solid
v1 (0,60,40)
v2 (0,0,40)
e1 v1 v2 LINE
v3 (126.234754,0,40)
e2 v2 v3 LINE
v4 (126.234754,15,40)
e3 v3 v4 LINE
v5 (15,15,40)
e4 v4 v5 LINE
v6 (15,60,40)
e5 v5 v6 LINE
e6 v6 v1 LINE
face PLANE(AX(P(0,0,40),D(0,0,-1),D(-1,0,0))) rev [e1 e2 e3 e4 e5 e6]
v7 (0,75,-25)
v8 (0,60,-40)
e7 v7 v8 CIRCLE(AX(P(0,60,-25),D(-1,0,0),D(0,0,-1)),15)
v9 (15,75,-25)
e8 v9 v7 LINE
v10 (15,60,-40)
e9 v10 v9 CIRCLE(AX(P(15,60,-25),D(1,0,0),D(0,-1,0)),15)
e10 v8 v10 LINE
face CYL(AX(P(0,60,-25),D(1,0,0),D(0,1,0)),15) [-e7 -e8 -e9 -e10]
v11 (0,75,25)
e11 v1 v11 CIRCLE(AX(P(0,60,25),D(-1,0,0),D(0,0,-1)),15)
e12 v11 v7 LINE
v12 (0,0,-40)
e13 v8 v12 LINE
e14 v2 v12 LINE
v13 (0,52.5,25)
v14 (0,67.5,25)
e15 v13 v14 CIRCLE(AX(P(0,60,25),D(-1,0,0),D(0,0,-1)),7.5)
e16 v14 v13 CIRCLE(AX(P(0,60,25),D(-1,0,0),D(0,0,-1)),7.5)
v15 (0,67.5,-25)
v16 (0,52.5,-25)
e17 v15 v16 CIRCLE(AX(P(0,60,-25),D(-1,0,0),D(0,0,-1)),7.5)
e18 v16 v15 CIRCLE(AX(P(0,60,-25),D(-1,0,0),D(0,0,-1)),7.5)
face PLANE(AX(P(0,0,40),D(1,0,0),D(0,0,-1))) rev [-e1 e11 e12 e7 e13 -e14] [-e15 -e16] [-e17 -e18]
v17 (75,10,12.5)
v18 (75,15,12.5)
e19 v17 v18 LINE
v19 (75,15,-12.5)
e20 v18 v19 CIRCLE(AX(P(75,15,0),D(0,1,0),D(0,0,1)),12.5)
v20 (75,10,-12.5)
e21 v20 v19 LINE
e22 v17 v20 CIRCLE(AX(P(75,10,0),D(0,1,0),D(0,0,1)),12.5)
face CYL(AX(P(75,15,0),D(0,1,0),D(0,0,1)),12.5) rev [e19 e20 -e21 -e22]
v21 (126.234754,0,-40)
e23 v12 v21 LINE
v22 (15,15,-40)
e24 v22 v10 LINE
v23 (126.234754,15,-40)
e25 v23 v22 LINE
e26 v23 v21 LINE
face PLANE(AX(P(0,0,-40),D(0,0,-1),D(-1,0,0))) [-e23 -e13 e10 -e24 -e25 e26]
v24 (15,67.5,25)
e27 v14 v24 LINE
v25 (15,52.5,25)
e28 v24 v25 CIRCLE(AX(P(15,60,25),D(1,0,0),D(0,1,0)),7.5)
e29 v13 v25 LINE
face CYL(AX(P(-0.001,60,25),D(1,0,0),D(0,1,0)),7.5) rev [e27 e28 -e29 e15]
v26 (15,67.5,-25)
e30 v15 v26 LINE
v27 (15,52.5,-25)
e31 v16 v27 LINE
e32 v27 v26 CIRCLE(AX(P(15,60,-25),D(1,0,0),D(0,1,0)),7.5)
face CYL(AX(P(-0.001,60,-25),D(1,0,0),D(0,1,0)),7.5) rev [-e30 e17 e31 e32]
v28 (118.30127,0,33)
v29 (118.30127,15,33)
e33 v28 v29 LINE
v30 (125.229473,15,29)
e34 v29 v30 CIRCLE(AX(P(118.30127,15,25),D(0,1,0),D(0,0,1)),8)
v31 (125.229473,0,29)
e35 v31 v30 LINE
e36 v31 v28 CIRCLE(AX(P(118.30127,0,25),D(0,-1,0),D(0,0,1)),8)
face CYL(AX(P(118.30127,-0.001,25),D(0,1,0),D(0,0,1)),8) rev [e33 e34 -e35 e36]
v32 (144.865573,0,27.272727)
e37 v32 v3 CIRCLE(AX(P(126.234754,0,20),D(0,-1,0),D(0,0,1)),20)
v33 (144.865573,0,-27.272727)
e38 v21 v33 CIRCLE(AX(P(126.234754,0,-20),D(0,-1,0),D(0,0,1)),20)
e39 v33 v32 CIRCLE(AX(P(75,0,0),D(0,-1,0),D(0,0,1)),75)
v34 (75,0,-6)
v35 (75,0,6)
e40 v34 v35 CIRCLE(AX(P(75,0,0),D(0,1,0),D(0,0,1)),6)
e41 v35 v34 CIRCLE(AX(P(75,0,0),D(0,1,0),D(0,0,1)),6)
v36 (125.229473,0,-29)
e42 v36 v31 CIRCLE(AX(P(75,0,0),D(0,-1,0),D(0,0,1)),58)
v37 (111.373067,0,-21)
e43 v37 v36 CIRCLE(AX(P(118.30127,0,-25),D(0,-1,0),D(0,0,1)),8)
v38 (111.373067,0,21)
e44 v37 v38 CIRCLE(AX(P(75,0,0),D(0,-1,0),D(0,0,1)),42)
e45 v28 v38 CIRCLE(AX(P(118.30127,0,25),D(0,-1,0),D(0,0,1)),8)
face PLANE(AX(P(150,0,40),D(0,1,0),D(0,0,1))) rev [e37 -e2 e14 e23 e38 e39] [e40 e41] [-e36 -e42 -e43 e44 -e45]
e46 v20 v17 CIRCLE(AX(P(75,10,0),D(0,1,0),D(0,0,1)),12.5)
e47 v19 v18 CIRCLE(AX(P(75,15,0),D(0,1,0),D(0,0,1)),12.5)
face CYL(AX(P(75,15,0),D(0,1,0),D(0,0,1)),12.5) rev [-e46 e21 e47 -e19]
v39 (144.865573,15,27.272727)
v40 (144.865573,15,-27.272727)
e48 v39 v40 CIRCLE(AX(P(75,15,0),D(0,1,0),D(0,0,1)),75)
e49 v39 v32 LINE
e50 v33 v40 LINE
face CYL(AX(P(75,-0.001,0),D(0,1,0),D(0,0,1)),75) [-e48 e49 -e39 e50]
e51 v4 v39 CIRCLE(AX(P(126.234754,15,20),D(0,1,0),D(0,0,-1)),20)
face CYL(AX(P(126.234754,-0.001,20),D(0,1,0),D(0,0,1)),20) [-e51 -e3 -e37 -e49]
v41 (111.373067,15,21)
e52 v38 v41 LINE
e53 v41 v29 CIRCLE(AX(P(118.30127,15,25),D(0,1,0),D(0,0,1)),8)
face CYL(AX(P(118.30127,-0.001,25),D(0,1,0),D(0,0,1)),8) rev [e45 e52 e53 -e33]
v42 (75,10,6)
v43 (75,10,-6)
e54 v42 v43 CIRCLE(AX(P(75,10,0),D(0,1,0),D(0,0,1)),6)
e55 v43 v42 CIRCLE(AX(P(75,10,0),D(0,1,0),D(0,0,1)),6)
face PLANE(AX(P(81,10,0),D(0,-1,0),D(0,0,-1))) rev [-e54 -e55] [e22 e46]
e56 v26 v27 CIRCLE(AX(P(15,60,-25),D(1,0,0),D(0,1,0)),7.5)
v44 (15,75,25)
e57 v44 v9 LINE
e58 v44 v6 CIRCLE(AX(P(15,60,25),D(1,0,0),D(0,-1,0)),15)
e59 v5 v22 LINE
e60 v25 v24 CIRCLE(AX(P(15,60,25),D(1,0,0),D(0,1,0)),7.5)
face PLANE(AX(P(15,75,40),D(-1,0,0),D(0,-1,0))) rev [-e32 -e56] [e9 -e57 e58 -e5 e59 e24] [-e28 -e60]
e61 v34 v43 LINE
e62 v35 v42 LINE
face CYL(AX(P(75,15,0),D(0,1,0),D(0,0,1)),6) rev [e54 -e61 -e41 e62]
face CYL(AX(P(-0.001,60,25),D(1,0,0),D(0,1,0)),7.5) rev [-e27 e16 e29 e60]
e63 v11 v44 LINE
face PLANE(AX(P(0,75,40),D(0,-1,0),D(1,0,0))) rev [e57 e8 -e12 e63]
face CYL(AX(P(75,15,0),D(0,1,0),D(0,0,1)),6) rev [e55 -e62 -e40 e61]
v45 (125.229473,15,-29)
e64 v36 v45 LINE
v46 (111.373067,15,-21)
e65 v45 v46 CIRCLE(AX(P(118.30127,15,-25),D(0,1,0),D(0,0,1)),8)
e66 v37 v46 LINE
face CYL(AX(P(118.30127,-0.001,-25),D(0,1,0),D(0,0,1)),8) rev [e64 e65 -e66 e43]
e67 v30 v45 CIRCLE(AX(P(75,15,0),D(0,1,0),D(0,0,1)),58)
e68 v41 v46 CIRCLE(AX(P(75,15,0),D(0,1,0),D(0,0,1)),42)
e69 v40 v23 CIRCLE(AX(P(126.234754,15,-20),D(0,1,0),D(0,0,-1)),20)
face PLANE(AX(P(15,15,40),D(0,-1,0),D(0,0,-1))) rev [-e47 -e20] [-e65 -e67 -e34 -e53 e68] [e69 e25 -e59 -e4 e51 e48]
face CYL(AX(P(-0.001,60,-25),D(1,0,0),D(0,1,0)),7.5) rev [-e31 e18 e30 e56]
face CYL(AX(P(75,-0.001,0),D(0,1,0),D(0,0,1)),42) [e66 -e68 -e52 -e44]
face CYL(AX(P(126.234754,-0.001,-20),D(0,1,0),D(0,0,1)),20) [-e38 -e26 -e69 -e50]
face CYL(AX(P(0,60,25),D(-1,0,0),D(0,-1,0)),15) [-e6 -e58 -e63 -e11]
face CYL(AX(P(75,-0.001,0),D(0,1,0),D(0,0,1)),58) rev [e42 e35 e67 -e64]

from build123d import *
from OCP.BRepFilletAPI import BRepFilletAPI_MakeFillet

# Parameters (mm, degrees)
L_BRACKET_BODY_DEPTH             = 40
ARC_SLOT_R50_30DEG_REACH         = 168.433
CORNER_ROUNDS_R1                 = 20
CORNER_ROUNDS_R2                 = 15
COUNTERBORED_HOLE_12_D           = 12
COUNTERBORED_HOLE_12_DEPTH       = 100
COUNTERBORED_HOLE_12_CBORE_D     = 25
COUNTERBORED_HOLE_12_CBORE_DEPTH = 5
UPRIGHT_HOLES_2X_REACH           = 161.531
UPRIGHT_HOLES_SKETCH_R           = 7.5


with BuildPart() as part:
    # L Profile Sketch → L Bracket Body (new, symmetric)
    with BuildSketch(Plane.XY):
        Polygon((0, 0), (0, 75), (15, 75), (15, 15), (150, 15), (150, 0), align=None)
    extrude(amount=L_BRACKET_BODY_DEPTH, both=True)

    # Arc Slot Sketch → Arc Slot R50 30deg (cut, up to next)
    with BuildSketch(Plane(origin=(0, 15, 0), x_dir=(1, 0, 0), z_dir=(0, 1, 0)), mode=Mode.PRIVATE) as arc_slot_r50_30deg_sk1:
        with BuildLine():
            Line((138.442887702, -40), (150, -40))
            Line((150, -40), (150, 0))
            ThreePointArc((150, 0), (147.052815967, -20.818062138), (138.442887702, -40))
        make_face()
    arc_slot_r50_30deg_tool1 = extrude(arc_slot_r50_30deg_sk1.sketch, amount=-ARC_SLOT_R50_30DEG_REACH, mode=Mode.PRIVATE) & part.part
    # Arc Slot Sketch → Arc Slot R50 30deg (cut, up to next)
    with BuildSketch(Plane(origin=(0, 15, 0), x_dir=(1, 0, 0), z_dir=(0, 1, 0)), mode=Mode.PRIVATE) as arc_slot_r50_30deg_sk2:
        with BuildLine():
            ThreePointArc((138.442887702, 40), (147.052815967, 20.818062138), (150, 0))
            Line((150, 0), (150, 40))
            Line((150, 40), (138.442887702, 40))
        make_face()
    arc_slot_r50_30deg_tool2 = extrude(arc_slot_r50_30deg_sk2.sketch, amount=-ARC_SLOT_R50_30DEG_REACH, mode=Mode.PRIVATE) & part.part
    # Arc Slot Sketch → Arc Slot R50 30deg (cut, up to next)
    with BuildSketch(Plane(origin=(0, 15, 0), x_dir=(1, 0, 0), z_dir=(0, 1, 0)), mode=Mode.PRIVATE) as arc_slot_r50_30deg_sk3:
        with BuildLine():
            ThreePointArc((125.229473419, -29), (133, 0), (125.229473419, 29))
            ThreePointArc((125.229473419, 29), (114.301270189, 31.92820323), (111.373066959, 21))
            ThreePointArc((111.373066959, 21), (117, 0), (111.373066959, -21))
            ThreePointArc((111.373066959, -21), (114.301270189, -31.92820323), (125.229473419, -29))
        make_face()
    arc_slot_r50_30deg_tool3 = extrude(arc_slot_r50_30deg_sk3.sketch, amount=-ARC_SLOT_R50_30DEG_REACH, mode=Mode.PRIVATE) & part.part
    add(arc_slot_r50_30deg_tool1.solids().sort_by_distance((146.584015, 15, 30.160634))[0], mode=Mode.SUBTRACT)
    add(arc_slot_r50_30deg_tool2.solids().sort_by_distance((146.584015, 15, -30.160634))[0], mode=Mode.SUBTRACT)
    add(arc_slot_r50_30deg_tool3.solids().sort_by_distance((121.886119, 15, 0))[0], mode=Mode.SUBTRACT)

    # Corner Rounds: one fillet with a radius per group of edges: ONE call of the kernel's fillet builder (fillet() takes one radius for all edges)
    corner_rounds_edges_1 = [part.edges().sort_by_distance(p)[0] for p in [
        (138.442887702, 7.5, 40),
        (138.442887702, 7.5, -40),
    ]]
    corner_rounds_edges_2 = [part.edges().sort_by_distance(p)[0] for p in [
        (7.5, 75, 40),
        (7.5, 75, -40),
    ]]
    corner_rounds = BRepFilletAPI_MakeFillet(part.part.solid().wrapped)
    for e in corner_rounds_edges_1:
        corner_rounds.Add(CORNER_ROUNDS_R1, e.wrapped)
    for e in corner_rounds_edges_2:
        corner_rounds.Add(CORNER_ROUNDS_R2, e.wrapped)
    add(Compound.cast(corner_rounds.Shape()), mode=Mode.REPLACE)

    # Counterbored Hole _12
    with Locations(Plane(origin=(0, 15, 0), x_dir=(1, 0, 0), z_dir=(0, 1, 0))):
        with Locations((75, 0)):
            CounterBoreHole(COUNTERBORED_HOLE_12_D / 2, COUNTERBORED_HOLE_12_CBORE_D / 2, COUNTERBORED_HOLE_12_CBORE_DEPTH, depth=COUNTERBORED_HOLE_12_DEPTH)

    # Upright Holes Sketch → Upright Holes 2x (cut, up to next)
    with BuildSketch(Plane(origin=(15, 0, 0), x_dir=(0, 0, -1), z_dir=(1, 0, 0)), mode=Mode.PRIVATE) as upright_holes_2x_sk1:
        with Locations(Location((-25, 60, 0), (0, 0, 90))):
            Circle(UPRIGHT_HOLES_SKETCH_R)
    upright_holes_2x_tool1 = extrude(upright_holes_2x_sk1.sketch, amount=-UPRIGHT_HOLES_2X_REACH, mode=Mode.PRIVATE) & part.part
    # Upright Holes Sketch → Upright Holes 2x (cut, up to next)
    with BuildSketch(Plane(origin=(15, 0, 0), x_dir=(0, 0, -1), z_dir=(1, 0, 0)), mode=Mode.PRIVATE) as upright_holes_2x_sk2:
        with Locations(Location((25, 60, 0), (0, 0, 90))):
            Circle(UPRIGHT_HOLES_SKETCH_R)
    upright_holes_2x_tool2 = extrude(upright_holes_2x_sk2.sketch, amount=-UPRIGHT_HOLES_2X_REACH, mode=Mode.PRIVATE) & part.part
    add(upright_holes_2x_tool1.solids().sort_by_distance((15, 60, 25))[0], mode=Mode.SUBTRACT)
    add(upright_holes_2x_tool2.solids().sort_by_distance((15, 60, -25))[0], mode=Mode.SUBTRACT)


solid = part.part
